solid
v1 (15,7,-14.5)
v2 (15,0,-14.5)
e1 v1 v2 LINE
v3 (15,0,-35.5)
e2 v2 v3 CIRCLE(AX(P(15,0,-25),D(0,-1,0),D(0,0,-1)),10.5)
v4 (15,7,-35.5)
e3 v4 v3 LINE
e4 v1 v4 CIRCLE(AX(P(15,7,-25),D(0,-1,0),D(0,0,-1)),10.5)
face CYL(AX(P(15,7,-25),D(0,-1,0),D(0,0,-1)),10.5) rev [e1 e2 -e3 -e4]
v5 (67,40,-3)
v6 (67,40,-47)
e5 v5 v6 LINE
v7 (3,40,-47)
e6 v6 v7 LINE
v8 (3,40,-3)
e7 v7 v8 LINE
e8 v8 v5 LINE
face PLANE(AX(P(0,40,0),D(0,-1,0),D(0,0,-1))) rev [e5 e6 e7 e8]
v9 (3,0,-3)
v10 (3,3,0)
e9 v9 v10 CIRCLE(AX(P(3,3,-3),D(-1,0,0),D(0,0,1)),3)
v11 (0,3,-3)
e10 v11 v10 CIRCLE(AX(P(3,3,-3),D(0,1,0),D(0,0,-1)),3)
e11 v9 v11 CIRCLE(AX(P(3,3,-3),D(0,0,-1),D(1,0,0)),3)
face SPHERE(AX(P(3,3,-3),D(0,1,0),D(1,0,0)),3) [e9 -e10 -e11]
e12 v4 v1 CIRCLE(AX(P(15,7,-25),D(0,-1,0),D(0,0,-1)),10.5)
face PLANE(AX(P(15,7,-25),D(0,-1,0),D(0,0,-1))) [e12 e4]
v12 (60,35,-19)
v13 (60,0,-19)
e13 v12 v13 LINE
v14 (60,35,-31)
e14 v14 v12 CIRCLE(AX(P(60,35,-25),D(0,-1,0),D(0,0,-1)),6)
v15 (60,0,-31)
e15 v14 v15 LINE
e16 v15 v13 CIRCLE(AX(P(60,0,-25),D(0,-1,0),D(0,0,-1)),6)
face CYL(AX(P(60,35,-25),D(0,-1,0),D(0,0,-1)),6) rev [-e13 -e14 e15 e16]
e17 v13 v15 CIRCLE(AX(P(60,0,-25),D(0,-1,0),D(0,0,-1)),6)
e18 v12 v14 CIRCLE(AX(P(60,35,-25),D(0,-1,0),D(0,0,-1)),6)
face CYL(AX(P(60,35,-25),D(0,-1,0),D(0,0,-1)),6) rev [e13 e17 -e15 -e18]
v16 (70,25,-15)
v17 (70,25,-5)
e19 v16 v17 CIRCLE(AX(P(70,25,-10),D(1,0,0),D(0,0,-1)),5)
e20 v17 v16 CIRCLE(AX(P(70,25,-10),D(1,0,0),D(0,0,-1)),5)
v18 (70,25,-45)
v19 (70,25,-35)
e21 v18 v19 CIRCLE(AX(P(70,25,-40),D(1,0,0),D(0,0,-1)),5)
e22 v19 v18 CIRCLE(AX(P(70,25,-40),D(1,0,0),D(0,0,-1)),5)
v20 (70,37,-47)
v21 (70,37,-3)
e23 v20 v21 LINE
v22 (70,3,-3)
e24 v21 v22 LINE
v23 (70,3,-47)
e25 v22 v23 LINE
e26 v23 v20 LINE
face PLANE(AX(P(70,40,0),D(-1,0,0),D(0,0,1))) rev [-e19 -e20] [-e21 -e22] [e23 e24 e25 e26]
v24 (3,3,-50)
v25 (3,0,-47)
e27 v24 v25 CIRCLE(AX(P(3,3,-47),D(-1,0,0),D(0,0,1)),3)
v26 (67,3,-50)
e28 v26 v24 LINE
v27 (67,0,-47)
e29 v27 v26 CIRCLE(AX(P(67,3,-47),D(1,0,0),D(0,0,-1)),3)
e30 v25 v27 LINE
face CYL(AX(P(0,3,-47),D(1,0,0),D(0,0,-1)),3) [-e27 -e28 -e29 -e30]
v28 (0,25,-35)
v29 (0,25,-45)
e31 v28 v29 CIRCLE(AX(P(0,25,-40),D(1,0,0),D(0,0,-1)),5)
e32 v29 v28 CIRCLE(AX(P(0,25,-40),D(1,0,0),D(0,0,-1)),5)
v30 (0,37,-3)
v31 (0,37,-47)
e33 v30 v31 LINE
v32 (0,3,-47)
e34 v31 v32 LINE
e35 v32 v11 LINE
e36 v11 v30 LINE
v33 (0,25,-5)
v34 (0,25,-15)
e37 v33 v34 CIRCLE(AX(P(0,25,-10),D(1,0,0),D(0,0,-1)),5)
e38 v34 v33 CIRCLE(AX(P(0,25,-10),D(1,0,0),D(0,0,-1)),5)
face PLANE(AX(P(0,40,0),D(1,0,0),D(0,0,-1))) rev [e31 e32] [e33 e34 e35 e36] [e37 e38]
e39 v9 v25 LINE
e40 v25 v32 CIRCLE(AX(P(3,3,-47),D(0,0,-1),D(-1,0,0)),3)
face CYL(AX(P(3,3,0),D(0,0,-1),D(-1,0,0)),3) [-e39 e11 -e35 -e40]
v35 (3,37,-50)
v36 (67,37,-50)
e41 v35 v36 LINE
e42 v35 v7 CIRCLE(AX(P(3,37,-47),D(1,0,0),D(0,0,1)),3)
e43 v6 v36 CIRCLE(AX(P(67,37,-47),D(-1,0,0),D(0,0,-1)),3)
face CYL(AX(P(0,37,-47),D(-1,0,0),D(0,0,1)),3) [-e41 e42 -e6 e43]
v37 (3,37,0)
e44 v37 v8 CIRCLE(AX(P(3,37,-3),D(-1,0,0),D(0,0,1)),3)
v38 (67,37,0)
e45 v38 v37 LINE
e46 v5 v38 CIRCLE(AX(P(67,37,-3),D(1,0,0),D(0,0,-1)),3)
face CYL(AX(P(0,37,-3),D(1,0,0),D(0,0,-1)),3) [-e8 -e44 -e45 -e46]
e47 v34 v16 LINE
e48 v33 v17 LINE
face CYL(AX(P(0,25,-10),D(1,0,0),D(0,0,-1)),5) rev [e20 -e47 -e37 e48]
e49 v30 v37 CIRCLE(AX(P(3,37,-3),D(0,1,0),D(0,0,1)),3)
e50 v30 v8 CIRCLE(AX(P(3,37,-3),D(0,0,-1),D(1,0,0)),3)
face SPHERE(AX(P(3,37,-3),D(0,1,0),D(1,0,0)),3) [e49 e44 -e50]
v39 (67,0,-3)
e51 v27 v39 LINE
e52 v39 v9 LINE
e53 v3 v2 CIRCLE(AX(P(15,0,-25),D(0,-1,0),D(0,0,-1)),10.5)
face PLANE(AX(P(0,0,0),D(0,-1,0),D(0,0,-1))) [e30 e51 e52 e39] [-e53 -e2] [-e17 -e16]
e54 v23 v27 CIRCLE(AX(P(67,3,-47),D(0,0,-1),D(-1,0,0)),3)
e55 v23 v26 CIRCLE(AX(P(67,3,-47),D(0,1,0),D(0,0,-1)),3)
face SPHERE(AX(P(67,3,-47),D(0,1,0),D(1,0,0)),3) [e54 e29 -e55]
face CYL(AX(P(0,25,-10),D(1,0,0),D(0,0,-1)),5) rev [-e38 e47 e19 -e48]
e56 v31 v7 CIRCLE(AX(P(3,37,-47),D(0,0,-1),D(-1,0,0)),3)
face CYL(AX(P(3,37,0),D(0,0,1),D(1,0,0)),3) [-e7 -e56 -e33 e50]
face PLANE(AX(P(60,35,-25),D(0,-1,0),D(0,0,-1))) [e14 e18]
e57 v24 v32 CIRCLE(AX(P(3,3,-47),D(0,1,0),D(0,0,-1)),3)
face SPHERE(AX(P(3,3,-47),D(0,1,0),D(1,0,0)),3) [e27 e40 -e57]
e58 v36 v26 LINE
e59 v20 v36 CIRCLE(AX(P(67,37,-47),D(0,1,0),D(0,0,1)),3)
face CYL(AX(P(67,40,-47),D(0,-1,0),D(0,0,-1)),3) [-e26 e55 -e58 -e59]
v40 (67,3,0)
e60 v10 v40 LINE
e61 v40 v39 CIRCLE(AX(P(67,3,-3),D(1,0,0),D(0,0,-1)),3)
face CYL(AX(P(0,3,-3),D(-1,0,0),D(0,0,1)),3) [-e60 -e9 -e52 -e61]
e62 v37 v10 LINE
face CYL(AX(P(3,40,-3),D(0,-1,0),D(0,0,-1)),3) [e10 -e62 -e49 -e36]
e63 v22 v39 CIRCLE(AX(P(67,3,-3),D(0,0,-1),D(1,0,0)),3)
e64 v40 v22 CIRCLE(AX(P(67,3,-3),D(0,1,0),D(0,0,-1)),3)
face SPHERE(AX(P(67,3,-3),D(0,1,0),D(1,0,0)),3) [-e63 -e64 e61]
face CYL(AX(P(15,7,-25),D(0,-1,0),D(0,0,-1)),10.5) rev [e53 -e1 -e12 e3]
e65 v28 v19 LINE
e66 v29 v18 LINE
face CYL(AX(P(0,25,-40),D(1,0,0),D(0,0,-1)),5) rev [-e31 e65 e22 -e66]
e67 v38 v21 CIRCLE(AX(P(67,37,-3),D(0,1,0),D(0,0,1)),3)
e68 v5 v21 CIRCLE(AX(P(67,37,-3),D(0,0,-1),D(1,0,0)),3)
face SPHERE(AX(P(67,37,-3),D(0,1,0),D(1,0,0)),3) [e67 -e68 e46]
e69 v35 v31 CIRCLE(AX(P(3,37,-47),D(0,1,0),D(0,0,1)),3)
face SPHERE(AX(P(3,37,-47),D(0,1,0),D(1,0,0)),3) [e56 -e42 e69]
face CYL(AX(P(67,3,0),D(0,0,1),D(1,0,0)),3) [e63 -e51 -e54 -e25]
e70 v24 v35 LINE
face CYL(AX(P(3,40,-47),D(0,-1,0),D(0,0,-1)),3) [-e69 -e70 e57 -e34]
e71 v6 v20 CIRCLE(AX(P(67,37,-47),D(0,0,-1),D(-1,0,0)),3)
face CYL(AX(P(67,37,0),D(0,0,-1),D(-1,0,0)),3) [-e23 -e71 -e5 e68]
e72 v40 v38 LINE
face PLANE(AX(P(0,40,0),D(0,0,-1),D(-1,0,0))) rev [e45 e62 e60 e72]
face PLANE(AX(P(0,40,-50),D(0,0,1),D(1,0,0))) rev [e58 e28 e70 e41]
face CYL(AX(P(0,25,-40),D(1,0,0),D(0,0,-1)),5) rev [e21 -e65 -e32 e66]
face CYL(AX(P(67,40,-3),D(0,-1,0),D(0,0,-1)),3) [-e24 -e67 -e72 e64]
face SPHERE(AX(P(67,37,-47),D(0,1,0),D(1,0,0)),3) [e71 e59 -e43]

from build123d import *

# Parameters (mm, degrees)
SKETCH1_W           = 70
SKETCH1_H           = 50
BOSS_EXTRUDE1_DEPTH = 40
SKETCH2_R           = 5
CUT_EXTRUDE1_DEPTH  = 95.868329805
SKETCH3_R           = 6
CUT_EXTRUDE2_DEPTH  = 35
SKETCH4_R           = 10.5
CUT_EXTRUDE3_DEPTH  = 7
FILLET1_R           = 3


with BuildPart() as part:
    # Sketch1 → Boss-Extrude1 (new body)
    with BuildSketch(Plane(origin=(0, 0, 0), x_dir=(1, 0, 0), z_dir=(0, 1, 0))):
        with Locations((35, 25)):
            Rectangle(SKETCH1_W, SKETCH1_H)
    extrude(amount=BOSS_EXTRUDE1_DEPTH)

    # Sketch2 → Cut-Extrude1 (cut, through all)
    with BuildSketch(Plane(origin=(70, 0, 0), x_dir=(0, 0, -1), z_dir=(1, 0, 0))):
        with Locations((40, 25)):
            Circle(SKETCH2_R)
        with Locations((10, 25)):
            Circle(SKETCH2_R)
    extrude(amount=-CUT_EXTRUDE1_DEPTH, mode=Mode.SUBTRACT)

    # Sketch3 → Cut-Extrude2 (cut)
    with BuildSketch(Plane.XZ):
        with Locations(Location((60, -25, 0), (0, 0, 270))):
            Circle(SKETCH3_R)
    extrude(amount=-CUT_EXTRUDE2_DEPTH, mode=Mode.SUBTRACT)

    # Sketch4 → Cut-Extrude3 (cut)
    with BuildSketch(Plane.XZ):
        with Locations(Location((15, -25, 0), (0, 0, 270))):
            Circle(SKETCH4_R)
    extrude(amount=-CUT_EXTRUDE3_DEPTH, mode=Mode.SUBTRACT)

    # Fillet1
    fillet1_edges = [part.edges().sort_by_distance(p)[0] for p in [
        (70, 40, -25),
        (35, 40, -50),
        (0, 40, -25),
        (35, 0, -50),
        (70, 0, -25),
        (35, 0, 0),
        (0, 0, -25),
        (35, 40, 0),
        (0, 20, -50),
        (70, 20, -50),
        (70, 20, 0),
        (0, 20, 0),
    ]]
    fillet(fillet1_edges, radius=FILLET1_R)


solid = part.part
